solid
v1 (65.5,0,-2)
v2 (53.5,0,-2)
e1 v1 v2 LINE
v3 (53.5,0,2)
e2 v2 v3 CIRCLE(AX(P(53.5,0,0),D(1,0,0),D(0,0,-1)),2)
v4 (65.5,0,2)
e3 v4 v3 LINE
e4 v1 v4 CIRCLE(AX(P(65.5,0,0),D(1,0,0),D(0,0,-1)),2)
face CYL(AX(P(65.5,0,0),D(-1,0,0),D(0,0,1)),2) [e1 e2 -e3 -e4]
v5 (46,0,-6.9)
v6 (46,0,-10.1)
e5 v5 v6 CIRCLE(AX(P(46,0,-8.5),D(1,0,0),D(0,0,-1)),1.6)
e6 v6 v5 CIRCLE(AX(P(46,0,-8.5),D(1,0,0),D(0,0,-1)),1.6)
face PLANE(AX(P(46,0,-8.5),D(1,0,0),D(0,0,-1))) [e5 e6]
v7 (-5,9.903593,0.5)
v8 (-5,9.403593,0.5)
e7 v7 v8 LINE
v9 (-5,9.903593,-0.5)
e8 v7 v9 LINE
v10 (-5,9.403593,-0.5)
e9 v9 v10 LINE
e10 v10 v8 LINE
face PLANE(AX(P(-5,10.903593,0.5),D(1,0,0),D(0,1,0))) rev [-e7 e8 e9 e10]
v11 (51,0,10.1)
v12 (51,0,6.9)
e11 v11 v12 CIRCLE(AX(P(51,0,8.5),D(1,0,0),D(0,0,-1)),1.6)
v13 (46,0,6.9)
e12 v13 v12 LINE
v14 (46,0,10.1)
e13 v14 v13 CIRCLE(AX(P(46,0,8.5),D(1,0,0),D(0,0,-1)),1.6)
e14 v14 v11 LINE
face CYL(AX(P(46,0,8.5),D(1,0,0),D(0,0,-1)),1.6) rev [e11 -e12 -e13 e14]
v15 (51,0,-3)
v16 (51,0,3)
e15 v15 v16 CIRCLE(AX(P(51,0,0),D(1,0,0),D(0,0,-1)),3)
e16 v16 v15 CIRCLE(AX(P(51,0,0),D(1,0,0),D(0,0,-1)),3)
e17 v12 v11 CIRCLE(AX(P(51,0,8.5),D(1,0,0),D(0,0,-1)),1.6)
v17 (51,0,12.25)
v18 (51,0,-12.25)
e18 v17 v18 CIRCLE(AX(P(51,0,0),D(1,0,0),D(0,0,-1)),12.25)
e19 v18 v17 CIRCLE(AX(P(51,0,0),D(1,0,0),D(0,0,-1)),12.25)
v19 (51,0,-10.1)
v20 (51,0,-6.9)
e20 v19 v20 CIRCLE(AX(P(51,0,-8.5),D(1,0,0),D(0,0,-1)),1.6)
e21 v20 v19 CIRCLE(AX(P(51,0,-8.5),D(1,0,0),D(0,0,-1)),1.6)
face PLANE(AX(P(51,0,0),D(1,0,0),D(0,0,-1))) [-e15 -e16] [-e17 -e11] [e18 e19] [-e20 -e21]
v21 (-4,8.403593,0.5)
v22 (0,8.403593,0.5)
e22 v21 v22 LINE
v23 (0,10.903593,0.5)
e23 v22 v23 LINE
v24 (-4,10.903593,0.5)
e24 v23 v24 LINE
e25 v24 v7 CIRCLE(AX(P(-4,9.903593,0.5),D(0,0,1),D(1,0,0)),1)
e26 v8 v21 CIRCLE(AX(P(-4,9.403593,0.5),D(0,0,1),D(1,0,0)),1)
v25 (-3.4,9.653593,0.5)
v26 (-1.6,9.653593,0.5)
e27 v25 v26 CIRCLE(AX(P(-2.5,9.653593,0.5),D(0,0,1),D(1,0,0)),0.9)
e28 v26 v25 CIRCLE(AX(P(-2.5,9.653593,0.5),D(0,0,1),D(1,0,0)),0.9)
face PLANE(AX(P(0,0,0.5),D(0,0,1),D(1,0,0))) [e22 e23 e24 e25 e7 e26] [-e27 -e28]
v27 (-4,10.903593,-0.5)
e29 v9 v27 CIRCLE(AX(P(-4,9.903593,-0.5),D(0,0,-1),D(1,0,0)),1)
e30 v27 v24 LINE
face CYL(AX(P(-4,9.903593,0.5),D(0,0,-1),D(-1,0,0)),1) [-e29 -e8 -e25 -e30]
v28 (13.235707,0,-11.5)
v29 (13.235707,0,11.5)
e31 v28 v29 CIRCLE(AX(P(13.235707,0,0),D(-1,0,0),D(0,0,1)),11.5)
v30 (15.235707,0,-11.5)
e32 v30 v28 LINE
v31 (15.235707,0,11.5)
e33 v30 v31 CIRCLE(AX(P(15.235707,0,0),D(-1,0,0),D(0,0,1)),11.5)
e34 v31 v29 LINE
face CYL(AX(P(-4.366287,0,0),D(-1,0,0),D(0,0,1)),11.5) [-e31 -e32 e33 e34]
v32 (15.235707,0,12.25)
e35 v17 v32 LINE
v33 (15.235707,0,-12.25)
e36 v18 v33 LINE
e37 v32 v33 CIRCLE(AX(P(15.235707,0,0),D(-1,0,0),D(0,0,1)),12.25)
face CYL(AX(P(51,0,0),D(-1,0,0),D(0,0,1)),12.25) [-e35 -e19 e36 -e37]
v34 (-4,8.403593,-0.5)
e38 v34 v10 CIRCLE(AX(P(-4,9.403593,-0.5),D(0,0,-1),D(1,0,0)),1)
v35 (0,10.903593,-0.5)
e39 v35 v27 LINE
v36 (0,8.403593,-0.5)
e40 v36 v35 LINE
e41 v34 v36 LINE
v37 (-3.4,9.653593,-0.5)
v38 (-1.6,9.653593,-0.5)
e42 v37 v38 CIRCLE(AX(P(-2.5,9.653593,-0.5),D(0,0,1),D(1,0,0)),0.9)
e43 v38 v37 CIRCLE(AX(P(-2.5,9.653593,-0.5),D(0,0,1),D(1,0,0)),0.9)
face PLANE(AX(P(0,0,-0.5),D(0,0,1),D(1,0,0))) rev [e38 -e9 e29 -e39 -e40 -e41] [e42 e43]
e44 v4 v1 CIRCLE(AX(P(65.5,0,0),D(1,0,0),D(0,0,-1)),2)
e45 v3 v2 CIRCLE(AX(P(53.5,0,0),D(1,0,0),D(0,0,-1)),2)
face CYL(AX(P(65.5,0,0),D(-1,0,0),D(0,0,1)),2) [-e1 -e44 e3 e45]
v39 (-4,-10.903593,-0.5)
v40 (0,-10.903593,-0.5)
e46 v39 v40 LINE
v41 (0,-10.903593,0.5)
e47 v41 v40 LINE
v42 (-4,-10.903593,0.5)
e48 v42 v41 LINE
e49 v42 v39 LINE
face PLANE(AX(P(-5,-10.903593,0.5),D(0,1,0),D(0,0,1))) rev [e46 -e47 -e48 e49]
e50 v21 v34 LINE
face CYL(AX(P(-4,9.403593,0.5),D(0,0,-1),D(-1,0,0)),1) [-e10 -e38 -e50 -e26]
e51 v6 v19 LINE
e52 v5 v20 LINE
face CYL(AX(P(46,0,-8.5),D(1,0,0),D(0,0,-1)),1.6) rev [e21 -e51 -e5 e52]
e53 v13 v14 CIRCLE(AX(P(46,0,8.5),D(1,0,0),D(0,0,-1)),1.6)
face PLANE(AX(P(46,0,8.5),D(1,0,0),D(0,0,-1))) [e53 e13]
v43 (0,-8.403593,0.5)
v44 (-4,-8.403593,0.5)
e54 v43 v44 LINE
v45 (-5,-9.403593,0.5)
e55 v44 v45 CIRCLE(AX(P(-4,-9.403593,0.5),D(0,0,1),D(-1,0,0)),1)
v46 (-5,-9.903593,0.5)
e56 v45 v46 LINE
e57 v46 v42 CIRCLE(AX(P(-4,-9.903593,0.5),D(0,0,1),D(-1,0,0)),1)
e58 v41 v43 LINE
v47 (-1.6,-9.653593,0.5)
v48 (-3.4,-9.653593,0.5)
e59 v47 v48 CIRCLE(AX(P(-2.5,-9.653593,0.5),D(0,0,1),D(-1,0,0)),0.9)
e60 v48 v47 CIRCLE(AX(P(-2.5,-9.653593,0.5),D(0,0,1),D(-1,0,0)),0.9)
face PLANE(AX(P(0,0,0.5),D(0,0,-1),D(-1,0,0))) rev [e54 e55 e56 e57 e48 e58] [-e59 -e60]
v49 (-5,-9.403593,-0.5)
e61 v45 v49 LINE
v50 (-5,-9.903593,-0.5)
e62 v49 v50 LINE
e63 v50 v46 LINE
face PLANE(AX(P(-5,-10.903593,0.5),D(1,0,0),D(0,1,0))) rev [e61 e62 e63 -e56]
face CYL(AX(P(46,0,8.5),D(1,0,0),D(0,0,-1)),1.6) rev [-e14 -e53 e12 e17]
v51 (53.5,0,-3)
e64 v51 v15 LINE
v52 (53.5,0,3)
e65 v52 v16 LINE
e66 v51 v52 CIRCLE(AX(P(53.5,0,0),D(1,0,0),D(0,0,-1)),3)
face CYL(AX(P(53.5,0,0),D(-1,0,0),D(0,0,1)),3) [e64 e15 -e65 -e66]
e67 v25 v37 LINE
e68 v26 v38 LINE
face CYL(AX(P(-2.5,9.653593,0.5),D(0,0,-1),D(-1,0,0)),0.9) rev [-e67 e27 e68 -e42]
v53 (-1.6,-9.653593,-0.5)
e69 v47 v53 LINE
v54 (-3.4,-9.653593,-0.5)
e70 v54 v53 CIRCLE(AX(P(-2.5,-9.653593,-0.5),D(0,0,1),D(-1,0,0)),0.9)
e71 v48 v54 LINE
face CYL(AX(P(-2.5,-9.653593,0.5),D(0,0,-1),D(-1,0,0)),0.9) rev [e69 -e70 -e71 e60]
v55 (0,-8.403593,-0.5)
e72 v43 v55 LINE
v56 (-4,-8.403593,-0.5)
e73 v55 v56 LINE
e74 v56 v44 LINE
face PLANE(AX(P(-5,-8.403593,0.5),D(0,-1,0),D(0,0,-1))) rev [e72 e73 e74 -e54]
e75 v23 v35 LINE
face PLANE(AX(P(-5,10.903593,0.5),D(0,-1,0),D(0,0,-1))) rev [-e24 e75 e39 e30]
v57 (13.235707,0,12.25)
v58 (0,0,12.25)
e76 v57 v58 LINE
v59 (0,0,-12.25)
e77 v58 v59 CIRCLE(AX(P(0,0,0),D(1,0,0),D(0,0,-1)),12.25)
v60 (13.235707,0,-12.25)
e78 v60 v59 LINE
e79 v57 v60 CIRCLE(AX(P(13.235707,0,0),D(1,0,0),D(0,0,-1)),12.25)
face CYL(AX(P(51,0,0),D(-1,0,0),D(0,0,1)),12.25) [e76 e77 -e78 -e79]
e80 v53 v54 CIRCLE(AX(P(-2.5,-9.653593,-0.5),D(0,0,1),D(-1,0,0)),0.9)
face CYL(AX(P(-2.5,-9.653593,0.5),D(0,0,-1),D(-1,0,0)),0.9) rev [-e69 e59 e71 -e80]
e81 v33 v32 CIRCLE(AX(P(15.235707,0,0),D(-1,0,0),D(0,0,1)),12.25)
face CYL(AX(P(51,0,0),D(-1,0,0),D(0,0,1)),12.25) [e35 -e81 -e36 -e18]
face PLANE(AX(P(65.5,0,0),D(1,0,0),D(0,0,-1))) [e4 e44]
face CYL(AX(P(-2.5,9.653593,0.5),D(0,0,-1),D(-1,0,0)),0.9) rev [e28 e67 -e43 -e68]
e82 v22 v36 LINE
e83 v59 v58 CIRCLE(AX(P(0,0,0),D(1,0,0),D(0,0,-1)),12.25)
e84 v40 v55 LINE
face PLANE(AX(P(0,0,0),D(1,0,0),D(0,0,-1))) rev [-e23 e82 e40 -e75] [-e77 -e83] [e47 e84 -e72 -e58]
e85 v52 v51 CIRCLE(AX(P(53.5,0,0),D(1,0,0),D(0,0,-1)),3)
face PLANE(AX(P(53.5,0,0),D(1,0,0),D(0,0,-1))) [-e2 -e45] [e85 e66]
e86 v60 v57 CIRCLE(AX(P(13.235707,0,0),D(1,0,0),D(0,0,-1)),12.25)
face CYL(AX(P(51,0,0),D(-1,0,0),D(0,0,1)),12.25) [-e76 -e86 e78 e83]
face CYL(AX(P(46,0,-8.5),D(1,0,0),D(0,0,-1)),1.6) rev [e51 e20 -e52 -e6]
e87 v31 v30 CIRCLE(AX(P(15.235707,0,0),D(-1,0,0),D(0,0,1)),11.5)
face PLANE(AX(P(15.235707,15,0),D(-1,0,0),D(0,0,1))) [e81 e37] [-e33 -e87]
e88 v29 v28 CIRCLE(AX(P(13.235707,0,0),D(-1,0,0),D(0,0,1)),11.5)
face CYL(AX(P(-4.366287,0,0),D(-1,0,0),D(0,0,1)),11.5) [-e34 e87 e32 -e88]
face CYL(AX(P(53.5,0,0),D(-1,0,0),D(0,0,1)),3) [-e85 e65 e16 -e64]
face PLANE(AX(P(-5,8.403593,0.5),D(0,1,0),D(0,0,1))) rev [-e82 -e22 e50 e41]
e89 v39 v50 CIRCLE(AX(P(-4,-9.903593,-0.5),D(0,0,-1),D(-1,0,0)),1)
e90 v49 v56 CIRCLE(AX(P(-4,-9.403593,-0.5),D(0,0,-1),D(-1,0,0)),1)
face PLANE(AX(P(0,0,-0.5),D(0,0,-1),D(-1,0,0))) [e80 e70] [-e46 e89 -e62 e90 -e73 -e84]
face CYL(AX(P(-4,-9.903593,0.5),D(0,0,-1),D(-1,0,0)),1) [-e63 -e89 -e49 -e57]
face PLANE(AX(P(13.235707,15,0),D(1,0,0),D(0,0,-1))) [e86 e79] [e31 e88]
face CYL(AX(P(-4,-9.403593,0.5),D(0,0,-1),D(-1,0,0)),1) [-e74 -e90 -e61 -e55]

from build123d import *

# Parameters (mm, degrees)
SKETCH4_R           = 12.25
BOSS_EXTRUDE1_DEPTH = 51
SKETCH5_W           = 5
SKETCH5_H           = 2.5
SKETCH5_R           = 0.9
BOSS_EXTRUDE2_DEPTH = 0.5
FILLET1_R           = 1
SKETCH6_R           = 3
BOSS_EXTRUDE3_DEPTH = 2.5
SKETCH7_R           = 2
BOSS_EXTRUDE4_DEPTH = 12
SKETCH8_W           = 2
SKETCH8_H           = 3.5
SKETCH9_R           = 1.6
CUT_EXTRUDE1_DEPTH  = 5


with BuildPart() as part:
    # Sketch4 → Boss-Extrude1 (new body)
    with BuildSketch(Plane(origin=(0, 0, 0), x_dir=(0, 0, -1), z_dir=(1, 0, 0))):
        Circle(SKETCH4_R)
    extrude(amount=BOSS_EXTRUDE1_DEPTH)

    # Sketch5 → Boss-Extrude2 (add, symmetric)
    # profile 1 of 2: a face of its own
    with BuildSketch(Plane.XY):
        with Locations((-2.5, 9.653593257)):
            Rectangle(SKETCH5_W, SKETCH5_H)
        with Locations((-2.5, 9.653593257)):
            Circle(SKETCH5_R, mode=Mode.SUBTRACT)
    # profile 2 of 2: a face of its own
    with BuildSketch(Plane.XY):
        with Locations((-2.5, -9.653593257)):
            Rectangle(SKETCH5_W, SKETCH5_H)
        with Locations(Location((-2.5, -9.653593257, 0), (0, 0, 180))):
            Circle(SKETCH5_R, mode=Mode.SUBTRACT)
    extrude(amount=BOSS_EXTRUDE2_DEPTH, both=True)

    # Fillet1
    fillet1_edges = [part.edges().sort_by_distance(p)[0] for p in [
        (-5, 8.403593257, 0),
        (-5, -8.403593257, 0),
        (-5, -10.903593257, 0),
        (-5, 10.903593257, 0),
    ]]
    fillet(fillet1_edges, radius=FILLET1_R)

    # Sketch6 → Boss-Extrude3 (add)
    with BuildSketch(Plane(origin=(51, 0, 0), x_dir=(0, 0, -1), z_dir=(1, 0, 0))):
        Circle(SKETCH6_R)
    extrude(amount=BOSS_EXTRUDE3_DEPTH)

    # Sketch7 → Boss-Extrude4 (add)
    with BuildSketch(Plane(origin=(53.5, 0, 0), x_dir=(0, 0, -1), z_dir=(1, 0, 0))):
        Circle(SKETCH7_R)
    extrude(amount=BOSS_EXTRUDE4_DEPTH)

    # Sketch8 → Cut-Revolve1 (revolve, cut)
    with BuildSketch(Plane.XY, mode=Mode.PRIVATE) as cut_revolve1_sk:
        with Locations((14.235706655, 13.25)):
            Rectangle(SKETCH8_W, SKETCH8_H)
    revolve(cut_revolve1_sk.sketch.rotate(Axis((-4.366287434, 0, 0), (1, 0, 0)), 90), axis=Axis((-4.366287434, 0, 0), (1, 0, 0)), mode=Mode.SUBTRACT)

    # Sketch9 → Cut-Extrude1 (cut)
    with BuildSketch(Plane(origin=(51, 0, 0), x_dir=(0, 0, -1), z_dir=(1, 0, 0))):
        with Locations((-8.5, 0)):
            Circle(SKETCH9_R)
        with Locations((8.5, 0)):
            Circle(SKETCH9_R)
    extrude(amount=-CUT_EXTRUDE1_DEPTH, mode=Mode.SUBTRACT)


solid = part.part
